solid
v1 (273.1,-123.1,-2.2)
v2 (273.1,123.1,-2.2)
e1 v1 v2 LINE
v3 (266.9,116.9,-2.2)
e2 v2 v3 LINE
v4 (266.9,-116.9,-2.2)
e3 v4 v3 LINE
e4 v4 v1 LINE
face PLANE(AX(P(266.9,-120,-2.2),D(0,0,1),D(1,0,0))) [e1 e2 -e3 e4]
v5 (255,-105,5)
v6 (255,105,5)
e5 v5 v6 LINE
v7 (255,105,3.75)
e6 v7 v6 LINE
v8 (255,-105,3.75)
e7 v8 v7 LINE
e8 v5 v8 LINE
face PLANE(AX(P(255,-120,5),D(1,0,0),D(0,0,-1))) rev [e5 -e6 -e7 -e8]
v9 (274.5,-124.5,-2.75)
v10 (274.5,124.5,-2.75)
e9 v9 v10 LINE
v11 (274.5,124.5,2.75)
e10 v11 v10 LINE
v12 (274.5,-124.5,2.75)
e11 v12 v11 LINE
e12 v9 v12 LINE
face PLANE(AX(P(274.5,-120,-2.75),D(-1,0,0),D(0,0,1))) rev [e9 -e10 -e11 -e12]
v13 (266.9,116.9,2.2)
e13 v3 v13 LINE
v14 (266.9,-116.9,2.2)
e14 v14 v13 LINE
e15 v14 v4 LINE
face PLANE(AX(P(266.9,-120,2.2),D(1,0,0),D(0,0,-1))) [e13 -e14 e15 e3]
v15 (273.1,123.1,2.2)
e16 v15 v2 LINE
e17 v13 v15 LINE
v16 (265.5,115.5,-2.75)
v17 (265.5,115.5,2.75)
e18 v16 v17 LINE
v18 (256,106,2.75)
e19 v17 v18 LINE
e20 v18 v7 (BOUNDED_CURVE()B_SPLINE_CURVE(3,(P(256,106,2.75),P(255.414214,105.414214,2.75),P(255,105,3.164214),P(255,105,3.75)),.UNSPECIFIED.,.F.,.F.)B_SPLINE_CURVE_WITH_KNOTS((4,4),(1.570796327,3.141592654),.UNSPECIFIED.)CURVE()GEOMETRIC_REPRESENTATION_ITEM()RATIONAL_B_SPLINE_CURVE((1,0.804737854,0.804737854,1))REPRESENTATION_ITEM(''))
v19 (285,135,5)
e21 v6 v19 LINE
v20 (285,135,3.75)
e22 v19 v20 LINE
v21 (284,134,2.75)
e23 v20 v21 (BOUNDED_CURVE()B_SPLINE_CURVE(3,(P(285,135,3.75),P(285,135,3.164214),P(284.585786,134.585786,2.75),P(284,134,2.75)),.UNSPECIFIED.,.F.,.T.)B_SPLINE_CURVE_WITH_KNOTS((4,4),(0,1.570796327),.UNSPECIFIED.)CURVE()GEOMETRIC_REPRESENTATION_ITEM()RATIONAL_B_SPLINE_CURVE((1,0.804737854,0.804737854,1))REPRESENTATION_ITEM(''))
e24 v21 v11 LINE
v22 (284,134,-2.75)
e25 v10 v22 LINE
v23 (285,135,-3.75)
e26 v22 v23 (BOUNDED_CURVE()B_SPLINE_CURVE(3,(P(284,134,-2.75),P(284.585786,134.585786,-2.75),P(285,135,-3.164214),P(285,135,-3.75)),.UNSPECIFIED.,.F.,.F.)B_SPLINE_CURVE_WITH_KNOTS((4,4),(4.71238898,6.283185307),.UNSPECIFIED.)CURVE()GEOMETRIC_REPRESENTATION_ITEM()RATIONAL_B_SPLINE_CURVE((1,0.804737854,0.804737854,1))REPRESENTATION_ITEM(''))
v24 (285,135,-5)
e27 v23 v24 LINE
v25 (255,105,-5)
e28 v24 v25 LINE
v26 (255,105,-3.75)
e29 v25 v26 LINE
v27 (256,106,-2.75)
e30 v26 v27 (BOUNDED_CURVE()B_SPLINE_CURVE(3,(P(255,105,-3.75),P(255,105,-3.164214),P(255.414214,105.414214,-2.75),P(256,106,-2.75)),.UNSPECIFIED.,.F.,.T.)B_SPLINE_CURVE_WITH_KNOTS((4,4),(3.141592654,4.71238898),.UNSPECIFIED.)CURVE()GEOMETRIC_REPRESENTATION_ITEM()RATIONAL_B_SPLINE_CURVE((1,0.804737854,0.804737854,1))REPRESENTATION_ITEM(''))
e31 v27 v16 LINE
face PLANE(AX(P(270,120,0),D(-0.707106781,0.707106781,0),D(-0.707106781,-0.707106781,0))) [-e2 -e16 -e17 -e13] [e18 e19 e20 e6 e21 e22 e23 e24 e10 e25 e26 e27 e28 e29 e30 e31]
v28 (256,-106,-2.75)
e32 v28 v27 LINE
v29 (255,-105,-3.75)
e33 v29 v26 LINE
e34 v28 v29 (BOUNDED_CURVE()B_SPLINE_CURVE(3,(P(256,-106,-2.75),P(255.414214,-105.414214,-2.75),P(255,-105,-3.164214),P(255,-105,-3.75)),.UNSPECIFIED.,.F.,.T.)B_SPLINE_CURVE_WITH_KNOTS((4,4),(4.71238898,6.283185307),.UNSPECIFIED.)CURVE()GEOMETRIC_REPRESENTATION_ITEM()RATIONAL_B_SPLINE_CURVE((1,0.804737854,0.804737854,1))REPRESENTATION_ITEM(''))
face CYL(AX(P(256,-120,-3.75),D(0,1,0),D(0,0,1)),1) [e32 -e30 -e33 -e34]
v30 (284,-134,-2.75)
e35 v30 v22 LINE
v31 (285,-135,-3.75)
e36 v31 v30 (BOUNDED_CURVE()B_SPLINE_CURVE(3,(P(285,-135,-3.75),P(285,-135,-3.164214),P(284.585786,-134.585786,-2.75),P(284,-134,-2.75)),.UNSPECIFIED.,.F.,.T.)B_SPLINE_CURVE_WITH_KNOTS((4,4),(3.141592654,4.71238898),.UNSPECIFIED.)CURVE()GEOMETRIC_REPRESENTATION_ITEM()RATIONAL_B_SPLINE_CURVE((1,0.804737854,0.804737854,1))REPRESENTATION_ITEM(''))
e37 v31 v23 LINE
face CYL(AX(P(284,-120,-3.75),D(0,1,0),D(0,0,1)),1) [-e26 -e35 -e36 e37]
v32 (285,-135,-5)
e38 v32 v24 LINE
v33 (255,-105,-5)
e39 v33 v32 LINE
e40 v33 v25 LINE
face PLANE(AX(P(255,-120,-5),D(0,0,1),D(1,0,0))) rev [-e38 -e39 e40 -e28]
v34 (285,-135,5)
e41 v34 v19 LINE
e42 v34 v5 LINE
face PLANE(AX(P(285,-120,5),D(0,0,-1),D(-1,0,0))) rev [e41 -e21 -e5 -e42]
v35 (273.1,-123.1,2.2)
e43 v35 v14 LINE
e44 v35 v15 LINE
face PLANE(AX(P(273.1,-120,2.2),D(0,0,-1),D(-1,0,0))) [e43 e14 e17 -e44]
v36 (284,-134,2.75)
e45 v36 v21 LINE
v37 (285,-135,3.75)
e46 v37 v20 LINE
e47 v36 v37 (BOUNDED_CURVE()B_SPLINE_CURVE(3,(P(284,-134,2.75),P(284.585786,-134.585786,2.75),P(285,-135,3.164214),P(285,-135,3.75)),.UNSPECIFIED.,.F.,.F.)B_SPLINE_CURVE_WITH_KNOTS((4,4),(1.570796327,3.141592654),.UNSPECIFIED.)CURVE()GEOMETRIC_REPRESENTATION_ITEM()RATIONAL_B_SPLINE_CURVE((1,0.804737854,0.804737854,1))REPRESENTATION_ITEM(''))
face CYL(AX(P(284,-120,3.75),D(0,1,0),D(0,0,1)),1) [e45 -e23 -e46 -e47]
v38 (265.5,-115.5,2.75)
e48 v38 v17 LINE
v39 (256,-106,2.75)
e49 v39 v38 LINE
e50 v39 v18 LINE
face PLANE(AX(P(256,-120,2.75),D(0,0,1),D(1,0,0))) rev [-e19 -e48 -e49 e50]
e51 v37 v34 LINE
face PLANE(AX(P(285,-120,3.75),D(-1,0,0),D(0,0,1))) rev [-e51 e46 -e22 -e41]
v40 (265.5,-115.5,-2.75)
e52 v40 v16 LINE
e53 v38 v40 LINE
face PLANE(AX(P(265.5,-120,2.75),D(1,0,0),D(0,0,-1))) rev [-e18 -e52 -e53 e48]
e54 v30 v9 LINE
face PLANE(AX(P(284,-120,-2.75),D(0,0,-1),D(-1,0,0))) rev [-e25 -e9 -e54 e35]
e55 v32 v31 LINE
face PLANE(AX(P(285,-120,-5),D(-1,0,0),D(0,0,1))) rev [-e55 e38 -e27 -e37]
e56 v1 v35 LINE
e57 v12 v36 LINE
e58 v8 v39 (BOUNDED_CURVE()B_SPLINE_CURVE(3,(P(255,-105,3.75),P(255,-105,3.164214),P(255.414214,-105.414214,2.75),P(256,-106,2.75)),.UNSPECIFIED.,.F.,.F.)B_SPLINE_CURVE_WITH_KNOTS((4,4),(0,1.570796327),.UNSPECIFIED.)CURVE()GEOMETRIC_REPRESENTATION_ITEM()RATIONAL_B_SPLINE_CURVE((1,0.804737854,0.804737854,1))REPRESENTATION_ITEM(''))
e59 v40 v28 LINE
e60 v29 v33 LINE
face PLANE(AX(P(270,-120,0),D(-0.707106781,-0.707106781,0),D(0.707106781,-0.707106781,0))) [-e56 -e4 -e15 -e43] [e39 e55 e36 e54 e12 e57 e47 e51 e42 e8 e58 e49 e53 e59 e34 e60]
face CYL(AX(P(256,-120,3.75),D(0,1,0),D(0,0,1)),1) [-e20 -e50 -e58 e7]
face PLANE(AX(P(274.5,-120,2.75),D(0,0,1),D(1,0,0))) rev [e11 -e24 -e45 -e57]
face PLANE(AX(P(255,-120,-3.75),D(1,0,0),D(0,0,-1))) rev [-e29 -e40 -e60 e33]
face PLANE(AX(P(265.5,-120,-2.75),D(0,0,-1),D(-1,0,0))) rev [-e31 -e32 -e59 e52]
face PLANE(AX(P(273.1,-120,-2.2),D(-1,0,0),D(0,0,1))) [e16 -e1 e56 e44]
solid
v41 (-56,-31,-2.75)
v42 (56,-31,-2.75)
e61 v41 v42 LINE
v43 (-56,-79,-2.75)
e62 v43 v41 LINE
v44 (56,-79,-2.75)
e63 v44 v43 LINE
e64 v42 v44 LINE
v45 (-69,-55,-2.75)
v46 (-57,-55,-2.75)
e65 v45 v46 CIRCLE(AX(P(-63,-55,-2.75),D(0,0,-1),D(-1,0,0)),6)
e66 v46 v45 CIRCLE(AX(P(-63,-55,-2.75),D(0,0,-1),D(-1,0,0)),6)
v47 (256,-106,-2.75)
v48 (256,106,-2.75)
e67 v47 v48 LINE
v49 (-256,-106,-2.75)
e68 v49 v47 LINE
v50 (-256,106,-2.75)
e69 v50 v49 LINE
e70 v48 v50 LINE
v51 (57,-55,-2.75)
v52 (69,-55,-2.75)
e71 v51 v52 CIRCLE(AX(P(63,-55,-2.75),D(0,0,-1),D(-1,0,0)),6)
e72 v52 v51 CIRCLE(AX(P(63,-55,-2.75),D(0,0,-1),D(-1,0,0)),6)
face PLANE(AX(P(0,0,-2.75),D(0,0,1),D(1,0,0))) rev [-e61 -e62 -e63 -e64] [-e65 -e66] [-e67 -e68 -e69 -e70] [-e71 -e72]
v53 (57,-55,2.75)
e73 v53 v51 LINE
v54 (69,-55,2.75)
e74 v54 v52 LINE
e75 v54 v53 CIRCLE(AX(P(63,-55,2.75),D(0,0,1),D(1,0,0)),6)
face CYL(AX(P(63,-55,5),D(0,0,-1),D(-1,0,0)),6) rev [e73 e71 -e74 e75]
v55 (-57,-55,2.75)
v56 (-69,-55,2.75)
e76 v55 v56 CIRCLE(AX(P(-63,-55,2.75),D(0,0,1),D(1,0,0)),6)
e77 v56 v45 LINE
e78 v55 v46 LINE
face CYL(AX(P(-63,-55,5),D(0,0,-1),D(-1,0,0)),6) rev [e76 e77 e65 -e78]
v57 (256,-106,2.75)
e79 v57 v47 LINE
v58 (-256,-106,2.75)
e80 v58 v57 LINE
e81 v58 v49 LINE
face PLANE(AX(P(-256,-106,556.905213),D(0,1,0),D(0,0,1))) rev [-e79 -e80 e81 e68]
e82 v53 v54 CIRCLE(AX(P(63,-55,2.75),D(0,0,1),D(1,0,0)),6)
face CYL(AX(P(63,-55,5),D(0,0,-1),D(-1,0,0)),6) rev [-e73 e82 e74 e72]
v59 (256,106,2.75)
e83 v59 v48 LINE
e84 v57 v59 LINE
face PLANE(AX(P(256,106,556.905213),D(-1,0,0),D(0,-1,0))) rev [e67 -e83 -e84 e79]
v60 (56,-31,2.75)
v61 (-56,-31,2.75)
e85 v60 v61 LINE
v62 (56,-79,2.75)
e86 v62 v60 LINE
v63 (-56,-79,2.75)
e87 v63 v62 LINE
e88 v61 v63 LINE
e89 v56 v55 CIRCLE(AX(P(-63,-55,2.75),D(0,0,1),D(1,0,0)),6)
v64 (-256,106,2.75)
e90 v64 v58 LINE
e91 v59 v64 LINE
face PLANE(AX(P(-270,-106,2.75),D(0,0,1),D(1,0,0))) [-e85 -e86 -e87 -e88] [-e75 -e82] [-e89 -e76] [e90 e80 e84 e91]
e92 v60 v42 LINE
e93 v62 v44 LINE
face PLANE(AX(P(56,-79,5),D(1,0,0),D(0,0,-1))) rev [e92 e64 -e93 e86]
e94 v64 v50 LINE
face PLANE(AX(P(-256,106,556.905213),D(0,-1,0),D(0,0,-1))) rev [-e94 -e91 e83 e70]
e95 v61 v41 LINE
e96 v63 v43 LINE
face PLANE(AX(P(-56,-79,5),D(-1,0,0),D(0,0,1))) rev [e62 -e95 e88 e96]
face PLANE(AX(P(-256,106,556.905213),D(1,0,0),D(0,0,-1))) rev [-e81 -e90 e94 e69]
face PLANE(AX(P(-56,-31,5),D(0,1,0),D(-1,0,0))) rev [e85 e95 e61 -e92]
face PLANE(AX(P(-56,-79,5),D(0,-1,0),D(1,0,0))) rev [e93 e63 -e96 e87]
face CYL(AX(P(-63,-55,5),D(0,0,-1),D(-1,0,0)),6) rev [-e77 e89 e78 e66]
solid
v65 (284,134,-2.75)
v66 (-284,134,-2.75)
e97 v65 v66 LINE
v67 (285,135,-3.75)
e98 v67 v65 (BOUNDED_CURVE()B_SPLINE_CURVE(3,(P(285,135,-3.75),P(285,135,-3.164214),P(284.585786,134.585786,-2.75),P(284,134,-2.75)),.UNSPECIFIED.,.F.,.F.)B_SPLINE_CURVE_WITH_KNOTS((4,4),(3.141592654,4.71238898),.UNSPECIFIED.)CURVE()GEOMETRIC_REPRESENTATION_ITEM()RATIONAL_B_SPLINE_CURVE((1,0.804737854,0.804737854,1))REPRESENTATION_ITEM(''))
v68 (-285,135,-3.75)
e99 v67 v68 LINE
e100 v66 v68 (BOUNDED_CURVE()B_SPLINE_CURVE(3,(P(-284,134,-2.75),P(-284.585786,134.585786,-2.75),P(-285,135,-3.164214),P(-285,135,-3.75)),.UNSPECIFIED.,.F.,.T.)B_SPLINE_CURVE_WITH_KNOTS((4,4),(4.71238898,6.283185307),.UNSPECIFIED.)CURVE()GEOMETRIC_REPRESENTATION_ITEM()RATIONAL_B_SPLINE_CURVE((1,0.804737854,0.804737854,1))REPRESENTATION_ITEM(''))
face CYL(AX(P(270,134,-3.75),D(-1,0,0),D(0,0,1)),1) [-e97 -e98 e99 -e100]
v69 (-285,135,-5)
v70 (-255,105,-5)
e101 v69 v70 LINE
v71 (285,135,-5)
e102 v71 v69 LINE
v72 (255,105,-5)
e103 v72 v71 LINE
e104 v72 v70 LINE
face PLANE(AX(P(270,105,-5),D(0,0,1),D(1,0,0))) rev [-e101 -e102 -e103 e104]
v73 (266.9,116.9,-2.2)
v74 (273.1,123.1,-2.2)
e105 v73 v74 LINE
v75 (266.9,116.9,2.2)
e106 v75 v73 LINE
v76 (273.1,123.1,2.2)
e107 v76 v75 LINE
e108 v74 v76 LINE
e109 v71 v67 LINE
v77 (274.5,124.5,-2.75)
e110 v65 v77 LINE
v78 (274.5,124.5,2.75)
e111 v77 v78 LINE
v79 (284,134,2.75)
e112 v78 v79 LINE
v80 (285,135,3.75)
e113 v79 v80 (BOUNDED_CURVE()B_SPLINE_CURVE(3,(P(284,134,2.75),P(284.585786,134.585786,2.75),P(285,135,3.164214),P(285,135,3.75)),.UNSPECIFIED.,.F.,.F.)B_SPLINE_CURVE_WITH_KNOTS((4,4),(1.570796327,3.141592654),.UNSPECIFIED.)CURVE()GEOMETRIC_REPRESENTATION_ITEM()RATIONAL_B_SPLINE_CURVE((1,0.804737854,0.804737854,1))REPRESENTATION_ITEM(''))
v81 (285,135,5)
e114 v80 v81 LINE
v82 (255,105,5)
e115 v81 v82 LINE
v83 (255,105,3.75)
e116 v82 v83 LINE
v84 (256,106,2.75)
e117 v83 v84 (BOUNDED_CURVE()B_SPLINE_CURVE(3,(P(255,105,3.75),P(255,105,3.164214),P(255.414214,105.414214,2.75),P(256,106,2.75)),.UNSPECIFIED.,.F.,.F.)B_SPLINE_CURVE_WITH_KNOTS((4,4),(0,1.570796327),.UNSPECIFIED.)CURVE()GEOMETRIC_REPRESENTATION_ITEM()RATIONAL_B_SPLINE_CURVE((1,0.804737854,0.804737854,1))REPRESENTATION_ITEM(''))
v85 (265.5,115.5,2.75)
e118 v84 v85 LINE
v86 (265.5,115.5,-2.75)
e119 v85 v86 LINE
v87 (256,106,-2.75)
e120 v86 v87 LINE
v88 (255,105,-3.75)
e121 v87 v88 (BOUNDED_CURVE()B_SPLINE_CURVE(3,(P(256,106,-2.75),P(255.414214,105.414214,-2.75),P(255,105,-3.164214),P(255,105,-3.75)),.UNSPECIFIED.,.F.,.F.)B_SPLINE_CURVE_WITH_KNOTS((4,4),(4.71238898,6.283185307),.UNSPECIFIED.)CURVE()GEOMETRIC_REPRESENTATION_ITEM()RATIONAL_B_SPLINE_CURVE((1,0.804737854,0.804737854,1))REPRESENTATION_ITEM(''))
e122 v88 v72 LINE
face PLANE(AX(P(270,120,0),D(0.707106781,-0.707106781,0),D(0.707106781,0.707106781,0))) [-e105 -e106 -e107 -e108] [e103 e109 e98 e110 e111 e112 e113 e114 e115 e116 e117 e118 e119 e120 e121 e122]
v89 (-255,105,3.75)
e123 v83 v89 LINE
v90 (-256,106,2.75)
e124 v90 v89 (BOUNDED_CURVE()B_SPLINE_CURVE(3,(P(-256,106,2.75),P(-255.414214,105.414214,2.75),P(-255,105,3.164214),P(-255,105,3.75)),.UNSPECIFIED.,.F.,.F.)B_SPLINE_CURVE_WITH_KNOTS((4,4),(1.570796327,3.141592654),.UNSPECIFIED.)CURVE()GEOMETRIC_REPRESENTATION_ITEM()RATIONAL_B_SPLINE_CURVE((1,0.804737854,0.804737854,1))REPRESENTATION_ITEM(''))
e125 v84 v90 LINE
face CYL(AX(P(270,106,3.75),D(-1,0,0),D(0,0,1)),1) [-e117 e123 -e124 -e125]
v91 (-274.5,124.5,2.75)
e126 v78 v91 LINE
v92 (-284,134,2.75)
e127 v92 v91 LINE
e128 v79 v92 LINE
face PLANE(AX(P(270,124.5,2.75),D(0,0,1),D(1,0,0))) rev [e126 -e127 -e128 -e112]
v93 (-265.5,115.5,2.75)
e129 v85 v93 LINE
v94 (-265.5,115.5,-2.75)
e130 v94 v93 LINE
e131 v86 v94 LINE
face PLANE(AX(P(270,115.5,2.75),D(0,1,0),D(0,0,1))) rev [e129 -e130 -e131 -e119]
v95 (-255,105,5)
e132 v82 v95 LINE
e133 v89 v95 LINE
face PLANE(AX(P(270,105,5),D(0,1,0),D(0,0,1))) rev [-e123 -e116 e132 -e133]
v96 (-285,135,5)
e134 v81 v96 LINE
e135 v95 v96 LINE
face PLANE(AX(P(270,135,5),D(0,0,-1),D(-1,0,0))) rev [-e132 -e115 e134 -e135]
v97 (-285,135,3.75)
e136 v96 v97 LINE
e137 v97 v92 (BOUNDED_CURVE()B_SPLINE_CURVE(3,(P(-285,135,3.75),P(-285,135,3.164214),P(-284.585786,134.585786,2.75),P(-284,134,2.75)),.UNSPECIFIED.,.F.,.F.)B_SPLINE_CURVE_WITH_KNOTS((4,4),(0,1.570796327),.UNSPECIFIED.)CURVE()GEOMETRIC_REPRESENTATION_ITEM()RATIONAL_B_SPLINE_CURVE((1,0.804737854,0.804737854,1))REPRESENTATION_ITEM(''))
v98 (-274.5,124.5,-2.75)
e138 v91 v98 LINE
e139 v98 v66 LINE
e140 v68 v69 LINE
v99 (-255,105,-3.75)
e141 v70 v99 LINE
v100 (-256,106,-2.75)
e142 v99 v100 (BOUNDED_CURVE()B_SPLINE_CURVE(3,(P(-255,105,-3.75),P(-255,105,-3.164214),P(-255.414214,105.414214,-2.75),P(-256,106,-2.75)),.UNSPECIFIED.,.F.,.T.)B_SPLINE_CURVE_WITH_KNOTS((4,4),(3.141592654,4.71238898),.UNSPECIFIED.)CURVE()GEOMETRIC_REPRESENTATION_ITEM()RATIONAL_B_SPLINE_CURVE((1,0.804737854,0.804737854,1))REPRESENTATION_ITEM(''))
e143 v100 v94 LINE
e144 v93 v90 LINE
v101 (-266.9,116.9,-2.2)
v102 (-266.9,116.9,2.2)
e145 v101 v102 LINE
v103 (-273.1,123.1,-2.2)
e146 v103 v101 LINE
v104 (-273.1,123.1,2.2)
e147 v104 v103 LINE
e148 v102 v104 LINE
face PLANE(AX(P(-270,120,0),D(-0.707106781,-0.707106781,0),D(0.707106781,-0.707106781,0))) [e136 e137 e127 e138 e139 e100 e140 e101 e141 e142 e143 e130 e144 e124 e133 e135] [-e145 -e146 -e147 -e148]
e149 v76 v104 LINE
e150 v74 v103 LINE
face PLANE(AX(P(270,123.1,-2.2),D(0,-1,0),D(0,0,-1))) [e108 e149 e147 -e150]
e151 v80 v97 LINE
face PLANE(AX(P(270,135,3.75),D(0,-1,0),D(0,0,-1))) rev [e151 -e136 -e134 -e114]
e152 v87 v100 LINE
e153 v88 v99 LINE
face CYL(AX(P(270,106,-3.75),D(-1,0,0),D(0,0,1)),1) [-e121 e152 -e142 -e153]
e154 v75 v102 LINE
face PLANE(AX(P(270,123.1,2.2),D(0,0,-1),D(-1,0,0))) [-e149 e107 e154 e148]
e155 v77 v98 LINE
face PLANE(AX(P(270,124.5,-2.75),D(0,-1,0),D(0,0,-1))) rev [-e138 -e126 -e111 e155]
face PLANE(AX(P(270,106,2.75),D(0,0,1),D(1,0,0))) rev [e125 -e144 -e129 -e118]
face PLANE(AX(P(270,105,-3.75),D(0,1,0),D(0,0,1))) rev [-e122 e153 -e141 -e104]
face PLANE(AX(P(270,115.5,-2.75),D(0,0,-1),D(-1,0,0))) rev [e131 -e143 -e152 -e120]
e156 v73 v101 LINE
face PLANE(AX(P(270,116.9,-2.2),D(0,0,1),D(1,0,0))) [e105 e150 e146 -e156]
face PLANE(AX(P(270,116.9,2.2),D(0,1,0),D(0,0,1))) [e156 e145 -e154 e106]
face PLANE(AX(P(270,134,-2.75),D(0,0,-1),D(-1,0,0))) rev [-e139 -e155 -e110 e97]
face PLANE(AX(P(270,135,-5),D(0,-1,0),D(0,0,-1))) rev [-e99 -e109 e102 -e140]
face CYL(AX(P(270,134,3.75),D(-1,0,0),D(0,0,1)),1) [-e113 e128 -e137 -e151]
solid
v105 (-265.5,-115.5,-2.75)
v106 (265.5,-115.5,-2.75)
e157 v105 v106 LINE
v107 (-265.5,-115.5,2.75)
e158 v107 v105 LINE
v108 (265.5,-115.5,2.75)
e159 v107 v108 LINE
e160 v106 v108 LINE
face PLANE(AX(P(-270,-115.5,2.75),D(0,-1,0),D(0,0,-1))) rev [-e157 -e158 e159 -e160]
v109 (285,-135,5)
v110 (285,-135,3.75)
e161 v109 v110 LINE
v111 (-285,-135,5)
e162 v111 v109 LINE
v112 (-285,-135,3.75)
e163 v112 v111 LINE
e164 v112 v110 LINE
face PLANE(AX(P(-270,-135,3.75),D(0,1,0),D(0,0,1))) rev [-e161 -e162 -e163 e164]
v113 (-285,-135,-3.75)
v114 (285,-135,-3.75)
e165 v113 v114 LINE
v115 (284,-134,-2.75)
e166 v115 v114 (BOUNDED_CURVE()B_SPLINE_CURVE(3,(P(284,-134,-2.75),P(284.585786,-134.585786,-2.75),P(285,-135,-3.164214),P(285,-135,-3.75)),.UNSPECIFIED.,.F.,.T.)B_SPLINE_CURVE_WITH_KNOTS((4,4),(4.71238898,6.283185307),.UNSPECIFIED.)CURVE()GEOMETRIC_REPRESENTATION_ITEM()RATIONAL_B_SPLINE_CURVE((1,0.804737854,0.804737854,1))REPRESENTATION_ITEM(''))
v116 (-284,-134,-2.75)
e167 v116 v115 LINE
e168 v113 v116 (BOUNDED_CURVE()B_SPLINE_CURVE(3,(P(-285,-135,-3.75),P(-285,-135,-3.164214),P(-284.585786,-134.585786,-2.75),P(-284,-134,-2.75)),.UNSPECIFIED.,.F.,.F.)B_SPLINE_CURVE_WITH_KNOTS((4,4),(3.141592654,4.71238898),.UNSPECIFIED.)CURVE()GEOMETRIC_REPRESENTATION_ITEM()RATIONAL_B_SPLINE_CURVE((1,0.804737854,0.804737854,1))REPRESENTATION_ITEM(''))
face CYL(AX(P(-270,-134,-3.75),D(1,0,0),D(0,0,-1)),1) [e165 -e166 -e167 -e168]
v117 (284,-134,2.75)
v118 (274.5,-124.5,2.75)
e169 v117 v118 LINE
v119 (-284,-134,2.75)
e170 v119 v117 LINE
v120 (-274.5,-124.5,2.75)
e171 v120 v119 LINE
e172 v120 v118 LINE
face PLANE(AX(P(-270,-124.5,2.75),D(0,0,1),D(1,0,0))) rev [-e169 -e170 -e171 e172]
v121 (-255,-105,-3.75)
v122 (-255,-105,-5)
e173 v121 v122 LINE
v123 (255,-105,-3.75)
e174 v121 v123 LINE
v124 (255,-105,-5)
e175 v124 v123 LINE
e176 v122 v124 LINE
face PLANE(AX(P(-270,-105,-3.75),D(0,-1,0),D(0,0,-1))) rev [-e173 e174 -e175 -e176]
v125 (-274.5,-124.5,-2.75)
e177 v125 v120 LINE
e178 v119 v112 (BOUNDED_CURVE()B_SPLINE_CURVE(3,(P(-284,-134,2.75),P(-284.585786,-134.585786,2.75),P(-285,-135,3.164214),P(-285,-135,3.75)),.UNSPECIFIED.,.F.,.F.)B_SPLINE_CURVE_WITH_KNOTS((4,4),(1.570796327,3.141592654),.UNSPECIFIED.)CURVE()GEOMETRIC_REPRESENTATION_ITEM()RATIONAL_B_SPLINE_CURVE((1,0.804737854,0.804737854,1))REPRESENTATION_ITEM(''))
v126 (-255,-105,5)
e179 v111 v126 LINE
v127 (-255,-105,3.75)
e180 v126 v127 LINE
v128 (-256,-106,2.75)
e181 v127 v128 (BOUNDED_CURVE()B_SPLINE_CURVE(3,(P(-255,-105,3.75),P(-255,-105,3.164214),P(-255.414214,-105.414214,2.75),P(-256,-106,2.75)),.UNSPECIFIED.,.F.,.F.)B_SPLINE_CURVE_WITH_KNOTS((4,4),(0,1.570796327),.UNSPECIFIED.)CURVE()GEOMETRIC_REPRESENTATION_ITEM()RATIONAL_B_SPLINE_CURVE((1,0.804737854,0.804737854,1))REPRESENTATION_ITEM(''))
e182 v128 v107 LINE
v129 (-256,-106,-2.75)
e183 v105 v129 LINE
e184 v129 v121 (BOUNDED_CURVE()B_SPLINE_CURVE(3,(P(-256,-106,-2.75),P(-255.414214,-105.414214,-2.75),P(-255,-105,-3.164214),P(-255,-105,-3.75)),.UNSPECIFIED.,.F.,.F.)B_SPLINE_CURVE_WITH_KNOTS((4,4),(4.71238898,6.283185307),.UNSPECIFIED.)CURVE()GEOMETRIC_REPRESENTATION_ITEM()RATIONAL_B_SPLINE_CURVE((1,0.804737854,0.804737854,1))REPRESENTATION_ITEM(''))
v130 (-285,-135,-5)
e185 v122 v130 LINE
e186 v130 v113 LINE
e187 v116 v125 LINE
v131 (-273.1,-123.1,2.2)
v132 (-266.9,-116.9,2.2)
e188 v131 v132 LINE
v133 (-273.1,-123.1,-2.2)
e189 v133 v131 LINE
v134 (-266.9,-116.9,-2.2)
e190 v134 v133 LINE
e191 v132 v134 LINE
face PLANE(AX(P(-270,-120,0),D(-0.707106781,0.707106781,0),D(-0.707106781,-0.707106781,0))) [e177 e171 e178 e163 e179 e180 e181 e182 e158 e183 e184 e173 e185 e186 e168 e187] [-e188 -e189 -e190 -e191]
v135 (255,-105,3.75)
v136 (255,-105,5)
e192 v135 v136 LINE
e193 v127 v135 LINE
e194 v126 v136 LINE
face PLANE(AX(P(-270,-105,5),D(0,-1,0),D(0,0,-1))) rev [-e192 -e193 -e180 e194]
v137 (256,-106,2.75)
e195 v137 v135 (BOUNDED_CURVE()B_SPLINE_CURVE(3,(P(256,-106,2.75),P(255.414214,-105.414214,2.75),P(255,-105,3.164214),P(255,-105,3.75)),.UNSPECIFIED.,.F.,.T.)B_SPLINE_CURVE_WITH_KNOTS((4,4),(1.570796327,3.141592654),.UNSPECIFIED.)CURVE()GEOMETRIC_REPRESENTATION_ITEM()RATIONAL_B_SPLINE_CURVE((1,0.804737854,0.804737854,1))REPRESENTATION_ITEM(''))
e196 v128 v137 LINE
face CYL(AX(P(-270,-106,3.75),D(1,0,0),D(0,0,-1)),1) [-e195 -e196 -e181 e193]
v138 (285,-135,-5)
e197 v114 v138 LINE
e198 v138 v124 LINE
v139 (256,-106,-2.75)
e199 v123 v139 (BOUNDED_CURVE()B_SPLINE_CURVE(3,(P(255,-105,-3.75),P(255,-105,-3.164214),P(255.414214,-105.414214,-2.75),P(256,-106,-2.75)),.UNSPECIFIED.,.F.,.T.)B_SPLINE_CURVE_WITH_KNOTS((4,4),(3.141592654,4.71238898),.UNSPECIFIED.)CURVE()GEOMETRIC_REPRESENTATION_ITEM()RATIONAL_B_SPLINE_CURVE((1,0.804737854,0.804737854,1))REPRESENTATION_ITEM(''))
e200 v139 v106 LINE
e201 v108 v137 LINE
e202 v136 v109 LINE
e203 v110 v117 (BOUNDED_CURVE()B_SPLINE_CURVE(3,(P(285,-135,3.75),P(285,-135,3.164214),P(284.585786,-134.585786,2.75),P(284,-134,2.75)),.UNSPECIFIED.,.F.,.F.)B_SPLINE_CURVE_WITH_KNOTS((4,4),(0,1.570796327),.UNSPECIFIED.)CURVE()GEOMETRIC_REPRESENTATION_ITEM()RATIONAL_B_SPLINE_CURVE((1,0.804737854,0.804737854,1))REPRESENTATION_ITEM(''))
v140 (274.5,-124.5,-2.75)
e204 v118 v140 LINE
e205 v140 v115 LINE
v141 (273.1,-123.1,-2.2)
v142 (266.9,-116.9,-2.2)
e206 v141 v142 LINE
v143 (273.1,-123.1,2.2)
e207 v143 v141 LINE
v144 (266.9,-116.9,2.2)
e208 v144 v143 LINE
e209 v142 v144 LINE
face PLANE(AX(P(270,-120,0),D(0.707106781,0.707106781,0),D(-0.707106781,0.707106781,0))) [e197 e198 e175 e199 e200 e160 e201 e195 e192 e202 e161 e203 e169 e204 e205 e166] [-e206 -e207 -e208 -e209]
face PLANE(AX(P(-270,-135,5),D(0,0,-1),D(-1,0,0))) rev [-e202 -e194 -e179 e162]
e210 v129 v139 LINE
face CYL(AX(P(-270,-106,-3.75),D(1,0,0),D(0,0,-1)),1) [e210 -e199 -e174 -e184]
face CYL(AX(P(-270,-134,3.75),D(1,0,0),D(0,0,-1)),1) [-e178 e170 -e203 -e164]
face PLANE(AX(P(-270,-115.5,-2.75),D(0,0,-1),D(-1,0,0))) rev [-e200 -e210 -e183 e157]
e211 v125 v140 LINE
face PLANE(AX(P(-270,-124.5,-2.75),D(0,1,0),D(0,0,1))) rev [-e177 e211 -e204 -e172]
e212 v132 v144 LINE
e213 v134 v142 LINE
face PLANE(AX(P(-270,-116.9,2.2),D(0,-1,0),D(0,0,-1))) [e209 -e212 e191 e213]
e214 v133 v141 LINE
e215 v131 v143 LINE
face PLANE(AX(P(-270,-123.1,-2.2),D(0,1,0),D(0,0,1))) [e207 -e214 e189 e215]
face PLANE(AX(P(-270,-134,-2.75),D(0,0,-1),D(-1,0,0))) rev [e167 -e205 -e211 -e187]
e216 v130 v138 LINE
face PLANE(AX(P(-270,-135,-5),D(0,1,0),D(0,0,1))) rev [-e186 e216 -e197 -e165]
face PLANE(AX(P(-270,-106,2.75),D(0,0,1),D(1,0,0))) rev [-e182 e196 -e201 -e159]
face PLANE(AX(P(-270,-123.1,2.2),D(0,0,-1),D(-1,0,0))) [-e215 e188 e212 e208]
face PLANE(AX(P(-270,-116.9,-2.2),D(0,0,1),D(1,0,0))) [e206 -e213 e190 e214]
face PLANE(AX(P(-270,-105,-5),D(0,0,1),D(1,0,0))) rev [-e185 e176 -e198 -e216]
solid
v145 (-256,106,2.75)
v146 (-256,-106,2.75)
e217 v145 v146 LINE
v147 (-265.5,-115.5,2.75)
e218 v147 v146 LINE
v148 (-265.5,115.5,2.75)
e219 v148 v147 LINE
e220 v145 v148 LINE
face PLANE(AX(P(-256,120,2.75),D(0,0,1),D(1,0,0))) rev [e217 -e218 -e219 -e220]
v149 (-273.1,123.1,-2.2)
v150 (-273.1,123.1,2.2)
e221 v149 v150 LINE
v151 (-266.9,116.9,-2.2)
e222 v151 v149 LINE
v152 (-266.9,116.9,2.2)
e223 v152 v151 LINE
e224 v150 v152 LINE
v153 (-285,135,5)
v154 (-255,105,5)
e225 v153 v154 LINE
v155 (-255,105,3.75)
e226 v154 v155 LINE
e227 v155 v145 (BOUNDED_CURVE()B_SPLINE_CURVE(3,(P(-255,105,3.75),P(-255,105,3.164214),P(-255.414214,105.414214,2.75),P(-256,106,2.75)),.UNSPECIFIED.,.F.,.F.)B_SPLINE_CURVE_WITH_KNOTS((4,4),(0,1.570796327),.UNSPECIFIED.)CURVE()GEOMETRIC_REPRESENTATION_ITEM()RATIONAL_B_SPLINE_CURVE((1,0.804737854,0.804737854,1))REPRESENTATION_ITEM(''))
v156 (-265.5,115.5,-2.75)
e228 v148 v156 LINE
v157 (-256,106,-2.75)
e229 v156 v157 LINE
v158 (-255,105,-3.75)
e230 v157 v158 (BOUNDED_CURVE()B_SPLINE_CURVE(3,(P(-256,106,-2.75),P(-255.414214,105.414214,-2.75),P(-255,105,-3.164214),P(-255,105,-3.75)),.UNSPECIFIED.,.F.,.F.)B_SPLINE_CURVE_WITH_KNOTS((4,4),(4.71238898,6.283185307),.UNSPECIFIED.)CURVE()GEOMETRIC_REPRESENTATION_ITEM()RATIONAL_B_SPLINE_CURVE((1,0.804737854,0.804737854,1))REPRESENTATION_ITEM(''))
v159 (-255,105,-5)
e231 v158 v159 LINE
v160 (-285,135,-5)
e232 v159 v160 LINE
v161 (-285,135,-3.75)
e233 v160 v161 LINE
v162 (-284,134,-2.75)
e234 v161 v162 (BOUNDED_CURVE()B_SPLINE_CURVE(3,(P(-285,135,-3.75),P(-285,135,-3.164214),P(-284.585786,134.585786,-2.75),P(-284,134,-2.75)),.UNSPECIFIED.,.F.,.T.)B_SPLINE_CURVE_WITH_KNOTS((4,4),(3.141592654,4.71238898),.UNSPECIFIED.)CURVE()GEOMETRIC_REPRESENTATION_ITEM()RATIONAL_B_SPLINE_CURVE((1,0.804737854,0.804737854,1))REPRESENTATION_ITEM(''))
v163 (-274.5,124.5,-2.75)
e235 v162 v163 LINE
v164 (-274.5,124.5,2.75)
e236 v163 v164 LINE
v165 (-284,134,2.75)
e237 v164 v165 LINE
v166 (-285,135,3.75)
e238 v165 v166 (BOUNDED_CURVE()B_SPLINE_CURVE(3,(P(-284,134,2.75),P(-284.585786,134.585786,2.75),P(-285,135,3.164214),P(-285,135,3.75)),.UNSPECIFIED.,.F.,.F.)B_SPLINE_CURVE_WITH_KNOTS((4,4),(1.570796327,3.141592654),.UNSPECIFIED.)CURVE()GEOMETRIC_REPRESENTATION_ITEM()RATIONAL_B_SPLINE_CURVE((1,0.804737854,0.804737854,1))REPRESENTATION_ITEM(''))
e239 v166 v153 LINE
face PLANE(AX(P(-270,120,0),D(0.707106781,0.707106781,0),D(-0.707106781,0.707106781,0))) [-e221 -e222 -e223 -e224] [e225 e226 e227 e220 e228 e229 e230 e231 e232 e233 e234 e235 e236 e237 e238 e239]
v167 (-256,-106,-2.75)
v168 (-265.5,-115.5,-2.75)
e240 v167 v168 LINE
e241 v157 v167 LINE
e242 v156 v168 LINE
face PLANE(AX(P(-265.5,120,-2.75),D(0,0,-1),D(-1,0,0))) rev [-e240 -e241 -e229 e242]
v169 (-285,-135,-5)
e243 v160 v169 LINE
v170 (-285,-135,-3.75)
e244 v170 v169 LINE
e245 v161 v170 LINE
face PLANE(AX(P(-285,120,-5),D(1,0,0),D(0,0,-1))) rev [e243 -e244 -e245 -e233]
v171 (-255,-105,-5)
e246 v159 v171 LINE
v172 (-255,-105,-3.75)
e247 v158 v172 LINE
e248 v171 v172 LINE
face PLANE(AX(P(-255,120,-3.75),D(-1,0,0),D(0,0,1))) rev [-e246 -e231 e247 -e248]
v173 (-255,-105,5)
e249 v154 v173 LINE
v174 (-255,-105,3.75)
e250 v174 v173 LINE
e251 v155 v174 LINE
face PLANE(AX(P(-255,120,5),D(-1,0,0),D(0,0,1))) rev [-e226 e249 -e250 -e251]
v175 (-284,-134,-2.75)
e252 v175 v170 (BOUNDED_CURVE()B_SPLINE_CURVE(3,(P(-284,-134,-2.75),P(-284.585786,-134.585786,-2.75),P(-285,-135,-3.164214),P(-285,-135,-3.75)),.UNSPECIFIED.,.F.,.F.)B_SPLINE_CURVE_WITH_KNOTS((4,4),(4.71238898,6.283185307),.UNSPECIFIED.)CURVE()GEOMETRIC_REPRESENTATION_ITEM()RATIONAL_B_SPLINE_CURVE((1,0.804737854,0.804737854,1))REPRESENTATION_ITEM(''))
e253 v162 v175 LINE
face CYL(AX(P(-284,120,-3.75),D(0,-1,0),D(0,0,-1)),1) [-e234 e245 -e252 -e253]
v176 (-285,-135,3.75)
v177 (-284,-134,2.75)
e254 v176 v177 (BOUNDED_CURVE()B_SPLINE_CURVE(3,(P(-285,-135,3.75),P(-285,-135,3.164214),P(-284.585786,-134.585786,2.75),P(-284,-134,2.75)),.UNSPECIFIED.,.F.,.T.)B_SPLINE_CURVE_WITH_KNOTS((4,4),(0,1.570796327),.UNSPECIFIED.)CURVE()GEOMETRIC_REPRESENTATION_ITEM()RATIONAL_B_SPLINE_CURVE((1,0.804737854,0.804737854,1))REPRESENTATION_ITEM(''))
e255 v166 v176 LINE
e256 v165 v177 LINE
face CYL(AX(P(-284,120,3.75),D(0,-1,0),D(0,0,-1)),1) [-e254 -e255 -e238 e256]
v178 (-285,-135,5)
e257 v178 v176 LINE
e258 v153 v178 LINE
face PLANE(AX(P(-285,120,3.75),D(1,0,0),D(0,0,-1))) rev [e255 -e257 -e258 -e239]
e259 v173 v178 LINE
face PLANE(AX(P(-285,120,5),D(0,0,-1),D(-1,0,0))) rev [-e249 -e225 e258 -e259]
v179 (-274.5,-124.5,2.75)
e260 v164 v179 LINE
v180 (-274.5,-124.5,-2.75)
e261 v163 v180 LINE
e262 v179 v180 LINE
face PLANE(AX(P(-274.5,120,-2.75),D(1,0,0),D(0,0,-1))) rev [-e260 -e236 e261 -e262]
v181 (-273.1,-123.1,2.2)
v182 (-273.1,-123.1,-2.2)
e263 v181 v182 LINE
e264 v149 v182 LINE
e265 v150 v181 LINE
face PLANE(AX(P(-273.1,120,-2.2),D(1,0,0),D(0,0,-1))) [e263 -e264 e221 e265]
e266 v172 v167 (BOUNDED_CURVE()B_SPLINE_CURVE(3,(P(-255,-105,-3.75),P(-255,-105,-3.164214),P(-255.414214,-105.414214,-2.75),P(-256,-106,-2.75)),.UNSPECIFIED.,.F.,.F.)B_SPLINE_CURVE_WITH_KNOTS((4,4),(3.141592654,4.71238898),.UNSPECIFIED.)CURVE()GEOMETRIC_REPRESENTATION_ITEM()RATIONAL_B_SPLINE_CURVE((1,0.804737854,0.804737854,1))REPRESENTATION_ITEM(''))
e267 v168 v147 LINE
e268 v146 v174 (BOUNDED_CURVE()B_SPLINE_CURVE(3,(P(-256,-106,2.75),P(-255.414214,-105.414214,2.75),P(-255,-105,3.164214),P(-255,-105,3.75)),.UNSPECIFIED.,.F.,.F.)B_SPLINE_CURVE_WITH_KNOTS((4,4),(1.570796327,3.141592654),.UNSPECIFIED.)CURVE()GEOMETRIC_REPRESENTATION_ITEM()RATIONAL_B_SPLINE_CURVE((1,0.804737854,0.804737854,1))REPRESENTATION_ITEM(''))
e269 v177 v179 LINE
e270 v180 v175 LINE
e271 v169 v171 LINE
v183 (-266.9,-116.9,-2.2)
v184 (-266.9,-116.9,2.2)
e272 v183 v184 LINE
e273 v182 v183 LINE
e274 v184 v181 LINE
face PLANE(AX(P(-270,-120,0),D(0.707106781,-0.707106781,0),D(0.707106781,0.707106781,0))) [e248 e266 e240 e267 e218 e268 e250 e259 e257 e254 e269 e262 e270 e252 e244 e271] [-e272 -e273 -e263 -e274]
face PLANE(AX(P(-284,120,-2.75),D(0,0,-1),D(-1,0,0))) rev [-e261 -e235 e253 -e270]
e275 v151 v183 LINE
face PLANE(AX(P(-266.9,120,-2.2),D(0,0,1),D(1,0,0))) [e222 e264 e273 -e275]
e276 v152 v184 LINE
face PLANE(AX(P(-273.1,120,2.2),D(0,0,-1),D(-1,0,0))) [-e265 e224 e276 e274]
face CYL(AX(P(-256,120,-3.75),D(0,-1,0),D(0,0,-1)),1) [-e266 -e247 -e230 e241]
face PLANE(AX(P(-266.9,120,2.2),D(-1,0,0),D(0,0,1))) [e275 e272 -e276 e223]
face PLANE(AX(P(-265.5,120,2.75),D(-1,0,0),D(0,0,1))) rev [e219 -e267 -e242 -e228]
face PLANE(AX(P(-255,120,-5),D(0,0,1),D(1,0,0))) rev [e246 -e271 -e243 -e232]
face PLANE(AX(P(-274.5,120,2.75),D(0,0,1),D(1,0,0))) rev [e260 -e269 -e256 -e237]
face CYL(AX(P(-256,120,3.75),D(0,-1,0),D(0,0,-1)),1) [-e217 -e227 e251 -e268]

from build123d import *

# Parameters (mm, degrees)
ALUMINIUM_PROFILE_20_X_20_X_2_1_DEPTH      = 556.811388301
ALUMINIUM_PROFILE_20_X_20_X_2_1_DEPTH_BACK = 16.811388301
SKETCH1_W                                  = 6.2
SKETCH1_H                                  = 4.4
SKETCH1_ON_SEGMENT_2_W                     = 6.2
SKETCH1_ON_SEGMENT_2_H                     = 4.4
ALUMINIUM_PROFILE_20_X_20_X_2_1_2_DEPTH    = 273.622776602
SKETCH1_ON_SEGMENT_3_W                     = 6.2
SKETCH1_ON_SEGMENT_3_H                     = 4.4
ALUMINIUM_PROFILE_20_X_20_X_2_1_3_DEPTH    = 573.622776602
SKETCH1_ON_SEGMENT_4_W                     = 6.2
SKETCH1_ON_SEGMENT_4_H                     = 4.4
ALUMINIUM_PROFILE_20_X_20_X_2_1_4_DEPTH    = 273.622776602
SKETCH3_W                                  = 512
SKETCH3_H                                  = 212
BOSS_EXTRUDE1_DEPTH                        = 5.5
SKETCH4_R                                  = 6
SKETCH4_W                                  = 112
SKETCH4_H                                  = 48
CUT_EXTRUDE1_DEPTH                         = 316.452155643


with BuildPart() as part:
    # Sketch1 → Aluminium profile 20 X 20 X 2(1) (new, two sides: drawn at the far end of the back side and taken through both)
    with BuildSketch(Plane(origin=(-270, 120, 0), x_dir=(0, 1, 0), z_dir=(1, 0, 0)).offset(-ALUMINIUM_PROFILE_20_X_20_X_2_1_DEPTH_BACK)):
        with BuildLine():
            Line((4.5, 2.75), (14, 2.75))
            ThreePointArc((14, 2.75), (14.707106781, 3.042893219), (15, 3.75))
            Line((15, 3.75), (15, 5))
            Line((15, 5), (-15, 5))
            Line((-15, 5), (-15, 3.75))
            ThreePointArc((-15, 3.75), (-14.707106781, 3.042893219), (-14, 2.75))
            Line((-14, 2.75), (-4.5, 2.75))
            Line((-4.5, 2.75), (-4.5, -2.75))
            Line((-4.5, -2.75), (-14, -2.75))
            ThreePointArc((-14, -2.75), (-14.707106781, -3.042893219), (-15, -3.75))
            Line((-15, -3.75), (-15, -5))
            Line((-15, -5), (15, -5))
            Line((15, -5), (15, -3.75))
            ThreePointArc((15, -3.75), (14.707106781, -3.042893219), (14, -2.75))
            Line((14, -2.75), (4.5, -2.75))
            Line((4.5, -2.75), (4.5, 2.75))
        make_face()
        Rectangle(SKETCH1_W, SKETCH1_H, mode=Mode.SUBTRACT)
    extrude(amount=ALUMINIUM_PROFILE_20_X_20_X_2_1_DEPTH + ALUMINIUM_PROFILE_20_X_20_X_2_1_DEPTH_BACK)

    # Aluminium profile 20 X 20 X 2(1) mitre 1
    split(bisect_by=Plane(origin=(-270, 120, 0), x_dir=(-0.707106781, 0.707106781, 0), z_dir=(0.707106781, 0.707106781, 0)), keep=Keep.TOP)

    # Aluminium profile 20 X 20 X 2(1) mitre 2
    split(bisect_by=Plane(origin=(270, 120, 0), x_dir=(-0.707106781, -0.707106781, 0), z_dir=(-0.707106781, 0.707106781, 0)), keep=Keep.TOP)


with BuildPart() as body_2:
    # Sketch1 on segment 2 (carried to segment 2) → Aluminium profile 20 X 20 X 2_1 2 (new body)
    with BuildSketch(Plane(origin=(270, 136.811388301, 0), x_dir=(1, 0, 0), z_dir=(0, -1, 0))):
        with BuildLine():
            Line((4.5, 2.75), (14, 2.75))
            ThreePointArc((14, 2.75), (14.707106781, 3.042893219), (15, 3.75))
            Line((15, 3.75), (15, 5))
            Line((15, 5), (-15, 5))
            Line((-15, 5), (-15, 3.75))
            ThreePointArc((-15, 3.75), (-14.707106781, 3.042893219), (-14, 2.75))
            Line((-14, 2.75), (-4.5, 2.75))
            Line((-4.5, 2.75), (-4.5, -2.75))
            Line((-4.5, -2.75), (-14, -2.75))
            ThreePointArc((-14, -2.75), (-14.707106781, -3.042893219), (-15, -3.75))
            Line((-15, -3.75), (-15, -5))
            Line((-15, -5), (15, -5))
            Line((15, -5), (15, -3.75))
            ThreePointArc((15, -3.75), (14.707106781, -3.042893219), (14, -2.75))
            Line((14, -2.75), (4.5, -2.75))
            Line((4.5, -2.75), (4.5, 2.75))
        make_face()
        Rectangle(SKETCH1_ON_SEGMENT_2_W, SKETCH1_ON_SEGMENT_2_H, mode=Mode.SUBTRACT)
    extrude(amount=ALUMINIUM_PROFILE_20_X_20_X_2_1_2_DEPTH)

    # Aluminium profile 20 X 20 X 2_1 2 mitre
    split(bisect_by=Plane(origin=(270, -120, 0), x_dir=(-0.707106781, 0.707106781, 0), z_dir=(0.707106781, 0.707106781, 0)), keep=Keep.TOP)

    # Aluminium profile 20 X 20 X 2_1 2 mi 2
    split(bisect_by=Plane(origin=(270, 120, 0), x_dir=(0.707106781, 0.707106781, 0), z_dir=(0.707106781, -0.707106781, 0)), keep=Keep.TOP)


with BuildPart() as body_3:
    # Sketch1 on segment 3 (carried to segment 3) → Aluminium profile 20 X 20 X 2_1 3 (new body)
    with BuildSketch(Plane(origin=(286.811388301, -120, 0), x_dir=(0, -1, 0), z_dir=(-1, 0, 0))):
        with BuildLine():
            Line((4.5, 2.75), (14, 2.75))
            ThreePointArc((14, 2.75), (14.707106781, 3.042893219), (15, 3.75))
            Line((15, 3.75), (15, 5))
            Line((15, 5), (-15, 5))
            Line((-15, 5), (-15, 3.75))
            ThreePointArc((-15, 3.75), (-14.707106781, 3.042893219), (-14, 2.75))
            Line((-14, 2.75), (-4.5, 2.75))
            Line((-4.5, 2.75), (-4.5, -2.75))
            Line((-4.5, -2.75), (-14, -2.75))
            ThreePointArc((-14, -2.75), (-14.707106781, -3.042893219), (-15, -3.75))
            Line((-15, -3.75), (-15, -5))
            Line((-15, -5), (15, -5))
            Line((15, -5), (15, -3.75))
            ThreePointArc((15, -3.75), (14.707106781, -3.042893219), (14, -2.75))
            Line((14, -2.75), (4.5, -2.75))
            Line((4.5, -2.75), (4.5, 2.75))
        make_face()
        Rectangle(SKETCH1_ON_SEGMENT_3_W, SKETCH1_ON_SEGMENT_3_H, mode=Mode.SUBTRACT)
    extrude(amount=ALUMINIUM_PROFILE_20_X_20_X_2_1_3_DEPTH)

    # Aluminium profile 20 X 20 X 2_1 3 mitre
    split(bisect_by=Plane(origin=(-270, -120, 0), x_dir=(0.707106781, 0.707106781, 0), z_dir=(0.707106781, -0.707106781, 0)), keep=Keep.TOP)

    # Aluminium profile 20 X 20 X 2_1 3 mi 2
    split(bisect_by=Plane(origin=(270, -120, 0), x_dir=(0.707106781, -0.707106781, 0), z_dir=(-0.707106781, -0.707106781, 0)), keep=Keep.TOP)


with BuildPart() as body_4:
    # Sketch1 on segment 4 (carried to segment 4) → Aluminium profile 20 X 20 X 2_1 4 (new body)
    with BuildSketch(Plane(origin=(-270, -136.811388301, 0), x_dir=(-1, 0, 0), z_dir=(0, 1, 0))):
        with BuildLine():
            Line((4.5, 2.75), (14, 2.75))
            ThreePointArc((14, 2.75), (14.707106781, 3.042893219), (15, 3.75))
            Line((15, 3.75), (15, 5))
            Line((15, 5), (-15, 5))
            Line((-15, 5), (-15, 3.75))
            ThreePointArc((-15, 3.75), (-14.707106781, 3.042893219), (-14, 2.75))
            Line((-14, 2.75), (-4.5, 2.75))
            Line((-4.5, 2.75), (-4.5, -2.75))
            Line((-4.5, -2.75), (-14, -2.75))
            ThreePointArc((-14, -2.75), (-14.707106781, -3.042893219), (-15, -3.75))
            Line((-15, -3.75), (-15, -5))
            Line((-15, -5), (15, -5))
            Line((15, -5), (15, -3.75))
            ThreePointArc((15, -3.75), (14.707106781, -3.042893219), (14, -2.75))
            Line((14, -2.75), (4.5, -2.75))
            Line((4.5, -2.75), (4.5, 2.75))
        make_face()
        Rectangle(SKETCH1_ON_SEGMENT_4_W, SKETCH1_ON_SEGMENT_4_H, mode=Mode.SUBTRACT)
    extrude(amount=ALUMINIUM_PROFILE_20_X_20_X_2_1_4_DEPTH)

    # Aluminium profile 20 X 20 X 2_1 4 mitre
    split(bisect_by=Plane(origin=(-270, -120, 0), x_dir=(-0.707106781, -0.707106781, 0), z_dir=(-0.707106781, 0.707106781, 0)), keep=Keep.TOP)

    # Aluminium profile 20 X 20 X 2_1 4 mi 2
    split(bisect_by=Plane(origin=(-270, 120, 0), x_dir=(0.707106781, -0.707106781, 0), z_dir=(-0.707106781, -0.707106781, 0)), keep=Keep.TOP)


with BuildPart() as body_5:
    # Sketch3 → Boss-Extrude1 (new body)
    with BuildSketch(Plane.XY.offset(-2.75)):
        Rectangle(SKETCH3_W, SKETCH3_H)
    extrude(amount=BOSS_EXTRUDE1_DEPTH)

    # Sketch4 → Cut-Extrude1 (cut, through all)
    with BuildSketch(Plane(origin=(0, 0, -2.75), x_dir=(-1, 0, 0), z_dir=(0, 0, -1))):
        with Locations((-63, -55)):
            Circle(SKETCH4_R)
        with Locations((63, -55)):
            Circle(SKETCH4_R)
        with Locations((0, -55)):
            Rectangle(SKETCH4_W, SKETCH4_H)
    extrude(amount=-CUT_EXTRUDE1_DEPTH, mode=Mode.SUBTRACT)


solid = Compound([part.part, body_2.part, body_3.part, body_4.part, body_5.part])
